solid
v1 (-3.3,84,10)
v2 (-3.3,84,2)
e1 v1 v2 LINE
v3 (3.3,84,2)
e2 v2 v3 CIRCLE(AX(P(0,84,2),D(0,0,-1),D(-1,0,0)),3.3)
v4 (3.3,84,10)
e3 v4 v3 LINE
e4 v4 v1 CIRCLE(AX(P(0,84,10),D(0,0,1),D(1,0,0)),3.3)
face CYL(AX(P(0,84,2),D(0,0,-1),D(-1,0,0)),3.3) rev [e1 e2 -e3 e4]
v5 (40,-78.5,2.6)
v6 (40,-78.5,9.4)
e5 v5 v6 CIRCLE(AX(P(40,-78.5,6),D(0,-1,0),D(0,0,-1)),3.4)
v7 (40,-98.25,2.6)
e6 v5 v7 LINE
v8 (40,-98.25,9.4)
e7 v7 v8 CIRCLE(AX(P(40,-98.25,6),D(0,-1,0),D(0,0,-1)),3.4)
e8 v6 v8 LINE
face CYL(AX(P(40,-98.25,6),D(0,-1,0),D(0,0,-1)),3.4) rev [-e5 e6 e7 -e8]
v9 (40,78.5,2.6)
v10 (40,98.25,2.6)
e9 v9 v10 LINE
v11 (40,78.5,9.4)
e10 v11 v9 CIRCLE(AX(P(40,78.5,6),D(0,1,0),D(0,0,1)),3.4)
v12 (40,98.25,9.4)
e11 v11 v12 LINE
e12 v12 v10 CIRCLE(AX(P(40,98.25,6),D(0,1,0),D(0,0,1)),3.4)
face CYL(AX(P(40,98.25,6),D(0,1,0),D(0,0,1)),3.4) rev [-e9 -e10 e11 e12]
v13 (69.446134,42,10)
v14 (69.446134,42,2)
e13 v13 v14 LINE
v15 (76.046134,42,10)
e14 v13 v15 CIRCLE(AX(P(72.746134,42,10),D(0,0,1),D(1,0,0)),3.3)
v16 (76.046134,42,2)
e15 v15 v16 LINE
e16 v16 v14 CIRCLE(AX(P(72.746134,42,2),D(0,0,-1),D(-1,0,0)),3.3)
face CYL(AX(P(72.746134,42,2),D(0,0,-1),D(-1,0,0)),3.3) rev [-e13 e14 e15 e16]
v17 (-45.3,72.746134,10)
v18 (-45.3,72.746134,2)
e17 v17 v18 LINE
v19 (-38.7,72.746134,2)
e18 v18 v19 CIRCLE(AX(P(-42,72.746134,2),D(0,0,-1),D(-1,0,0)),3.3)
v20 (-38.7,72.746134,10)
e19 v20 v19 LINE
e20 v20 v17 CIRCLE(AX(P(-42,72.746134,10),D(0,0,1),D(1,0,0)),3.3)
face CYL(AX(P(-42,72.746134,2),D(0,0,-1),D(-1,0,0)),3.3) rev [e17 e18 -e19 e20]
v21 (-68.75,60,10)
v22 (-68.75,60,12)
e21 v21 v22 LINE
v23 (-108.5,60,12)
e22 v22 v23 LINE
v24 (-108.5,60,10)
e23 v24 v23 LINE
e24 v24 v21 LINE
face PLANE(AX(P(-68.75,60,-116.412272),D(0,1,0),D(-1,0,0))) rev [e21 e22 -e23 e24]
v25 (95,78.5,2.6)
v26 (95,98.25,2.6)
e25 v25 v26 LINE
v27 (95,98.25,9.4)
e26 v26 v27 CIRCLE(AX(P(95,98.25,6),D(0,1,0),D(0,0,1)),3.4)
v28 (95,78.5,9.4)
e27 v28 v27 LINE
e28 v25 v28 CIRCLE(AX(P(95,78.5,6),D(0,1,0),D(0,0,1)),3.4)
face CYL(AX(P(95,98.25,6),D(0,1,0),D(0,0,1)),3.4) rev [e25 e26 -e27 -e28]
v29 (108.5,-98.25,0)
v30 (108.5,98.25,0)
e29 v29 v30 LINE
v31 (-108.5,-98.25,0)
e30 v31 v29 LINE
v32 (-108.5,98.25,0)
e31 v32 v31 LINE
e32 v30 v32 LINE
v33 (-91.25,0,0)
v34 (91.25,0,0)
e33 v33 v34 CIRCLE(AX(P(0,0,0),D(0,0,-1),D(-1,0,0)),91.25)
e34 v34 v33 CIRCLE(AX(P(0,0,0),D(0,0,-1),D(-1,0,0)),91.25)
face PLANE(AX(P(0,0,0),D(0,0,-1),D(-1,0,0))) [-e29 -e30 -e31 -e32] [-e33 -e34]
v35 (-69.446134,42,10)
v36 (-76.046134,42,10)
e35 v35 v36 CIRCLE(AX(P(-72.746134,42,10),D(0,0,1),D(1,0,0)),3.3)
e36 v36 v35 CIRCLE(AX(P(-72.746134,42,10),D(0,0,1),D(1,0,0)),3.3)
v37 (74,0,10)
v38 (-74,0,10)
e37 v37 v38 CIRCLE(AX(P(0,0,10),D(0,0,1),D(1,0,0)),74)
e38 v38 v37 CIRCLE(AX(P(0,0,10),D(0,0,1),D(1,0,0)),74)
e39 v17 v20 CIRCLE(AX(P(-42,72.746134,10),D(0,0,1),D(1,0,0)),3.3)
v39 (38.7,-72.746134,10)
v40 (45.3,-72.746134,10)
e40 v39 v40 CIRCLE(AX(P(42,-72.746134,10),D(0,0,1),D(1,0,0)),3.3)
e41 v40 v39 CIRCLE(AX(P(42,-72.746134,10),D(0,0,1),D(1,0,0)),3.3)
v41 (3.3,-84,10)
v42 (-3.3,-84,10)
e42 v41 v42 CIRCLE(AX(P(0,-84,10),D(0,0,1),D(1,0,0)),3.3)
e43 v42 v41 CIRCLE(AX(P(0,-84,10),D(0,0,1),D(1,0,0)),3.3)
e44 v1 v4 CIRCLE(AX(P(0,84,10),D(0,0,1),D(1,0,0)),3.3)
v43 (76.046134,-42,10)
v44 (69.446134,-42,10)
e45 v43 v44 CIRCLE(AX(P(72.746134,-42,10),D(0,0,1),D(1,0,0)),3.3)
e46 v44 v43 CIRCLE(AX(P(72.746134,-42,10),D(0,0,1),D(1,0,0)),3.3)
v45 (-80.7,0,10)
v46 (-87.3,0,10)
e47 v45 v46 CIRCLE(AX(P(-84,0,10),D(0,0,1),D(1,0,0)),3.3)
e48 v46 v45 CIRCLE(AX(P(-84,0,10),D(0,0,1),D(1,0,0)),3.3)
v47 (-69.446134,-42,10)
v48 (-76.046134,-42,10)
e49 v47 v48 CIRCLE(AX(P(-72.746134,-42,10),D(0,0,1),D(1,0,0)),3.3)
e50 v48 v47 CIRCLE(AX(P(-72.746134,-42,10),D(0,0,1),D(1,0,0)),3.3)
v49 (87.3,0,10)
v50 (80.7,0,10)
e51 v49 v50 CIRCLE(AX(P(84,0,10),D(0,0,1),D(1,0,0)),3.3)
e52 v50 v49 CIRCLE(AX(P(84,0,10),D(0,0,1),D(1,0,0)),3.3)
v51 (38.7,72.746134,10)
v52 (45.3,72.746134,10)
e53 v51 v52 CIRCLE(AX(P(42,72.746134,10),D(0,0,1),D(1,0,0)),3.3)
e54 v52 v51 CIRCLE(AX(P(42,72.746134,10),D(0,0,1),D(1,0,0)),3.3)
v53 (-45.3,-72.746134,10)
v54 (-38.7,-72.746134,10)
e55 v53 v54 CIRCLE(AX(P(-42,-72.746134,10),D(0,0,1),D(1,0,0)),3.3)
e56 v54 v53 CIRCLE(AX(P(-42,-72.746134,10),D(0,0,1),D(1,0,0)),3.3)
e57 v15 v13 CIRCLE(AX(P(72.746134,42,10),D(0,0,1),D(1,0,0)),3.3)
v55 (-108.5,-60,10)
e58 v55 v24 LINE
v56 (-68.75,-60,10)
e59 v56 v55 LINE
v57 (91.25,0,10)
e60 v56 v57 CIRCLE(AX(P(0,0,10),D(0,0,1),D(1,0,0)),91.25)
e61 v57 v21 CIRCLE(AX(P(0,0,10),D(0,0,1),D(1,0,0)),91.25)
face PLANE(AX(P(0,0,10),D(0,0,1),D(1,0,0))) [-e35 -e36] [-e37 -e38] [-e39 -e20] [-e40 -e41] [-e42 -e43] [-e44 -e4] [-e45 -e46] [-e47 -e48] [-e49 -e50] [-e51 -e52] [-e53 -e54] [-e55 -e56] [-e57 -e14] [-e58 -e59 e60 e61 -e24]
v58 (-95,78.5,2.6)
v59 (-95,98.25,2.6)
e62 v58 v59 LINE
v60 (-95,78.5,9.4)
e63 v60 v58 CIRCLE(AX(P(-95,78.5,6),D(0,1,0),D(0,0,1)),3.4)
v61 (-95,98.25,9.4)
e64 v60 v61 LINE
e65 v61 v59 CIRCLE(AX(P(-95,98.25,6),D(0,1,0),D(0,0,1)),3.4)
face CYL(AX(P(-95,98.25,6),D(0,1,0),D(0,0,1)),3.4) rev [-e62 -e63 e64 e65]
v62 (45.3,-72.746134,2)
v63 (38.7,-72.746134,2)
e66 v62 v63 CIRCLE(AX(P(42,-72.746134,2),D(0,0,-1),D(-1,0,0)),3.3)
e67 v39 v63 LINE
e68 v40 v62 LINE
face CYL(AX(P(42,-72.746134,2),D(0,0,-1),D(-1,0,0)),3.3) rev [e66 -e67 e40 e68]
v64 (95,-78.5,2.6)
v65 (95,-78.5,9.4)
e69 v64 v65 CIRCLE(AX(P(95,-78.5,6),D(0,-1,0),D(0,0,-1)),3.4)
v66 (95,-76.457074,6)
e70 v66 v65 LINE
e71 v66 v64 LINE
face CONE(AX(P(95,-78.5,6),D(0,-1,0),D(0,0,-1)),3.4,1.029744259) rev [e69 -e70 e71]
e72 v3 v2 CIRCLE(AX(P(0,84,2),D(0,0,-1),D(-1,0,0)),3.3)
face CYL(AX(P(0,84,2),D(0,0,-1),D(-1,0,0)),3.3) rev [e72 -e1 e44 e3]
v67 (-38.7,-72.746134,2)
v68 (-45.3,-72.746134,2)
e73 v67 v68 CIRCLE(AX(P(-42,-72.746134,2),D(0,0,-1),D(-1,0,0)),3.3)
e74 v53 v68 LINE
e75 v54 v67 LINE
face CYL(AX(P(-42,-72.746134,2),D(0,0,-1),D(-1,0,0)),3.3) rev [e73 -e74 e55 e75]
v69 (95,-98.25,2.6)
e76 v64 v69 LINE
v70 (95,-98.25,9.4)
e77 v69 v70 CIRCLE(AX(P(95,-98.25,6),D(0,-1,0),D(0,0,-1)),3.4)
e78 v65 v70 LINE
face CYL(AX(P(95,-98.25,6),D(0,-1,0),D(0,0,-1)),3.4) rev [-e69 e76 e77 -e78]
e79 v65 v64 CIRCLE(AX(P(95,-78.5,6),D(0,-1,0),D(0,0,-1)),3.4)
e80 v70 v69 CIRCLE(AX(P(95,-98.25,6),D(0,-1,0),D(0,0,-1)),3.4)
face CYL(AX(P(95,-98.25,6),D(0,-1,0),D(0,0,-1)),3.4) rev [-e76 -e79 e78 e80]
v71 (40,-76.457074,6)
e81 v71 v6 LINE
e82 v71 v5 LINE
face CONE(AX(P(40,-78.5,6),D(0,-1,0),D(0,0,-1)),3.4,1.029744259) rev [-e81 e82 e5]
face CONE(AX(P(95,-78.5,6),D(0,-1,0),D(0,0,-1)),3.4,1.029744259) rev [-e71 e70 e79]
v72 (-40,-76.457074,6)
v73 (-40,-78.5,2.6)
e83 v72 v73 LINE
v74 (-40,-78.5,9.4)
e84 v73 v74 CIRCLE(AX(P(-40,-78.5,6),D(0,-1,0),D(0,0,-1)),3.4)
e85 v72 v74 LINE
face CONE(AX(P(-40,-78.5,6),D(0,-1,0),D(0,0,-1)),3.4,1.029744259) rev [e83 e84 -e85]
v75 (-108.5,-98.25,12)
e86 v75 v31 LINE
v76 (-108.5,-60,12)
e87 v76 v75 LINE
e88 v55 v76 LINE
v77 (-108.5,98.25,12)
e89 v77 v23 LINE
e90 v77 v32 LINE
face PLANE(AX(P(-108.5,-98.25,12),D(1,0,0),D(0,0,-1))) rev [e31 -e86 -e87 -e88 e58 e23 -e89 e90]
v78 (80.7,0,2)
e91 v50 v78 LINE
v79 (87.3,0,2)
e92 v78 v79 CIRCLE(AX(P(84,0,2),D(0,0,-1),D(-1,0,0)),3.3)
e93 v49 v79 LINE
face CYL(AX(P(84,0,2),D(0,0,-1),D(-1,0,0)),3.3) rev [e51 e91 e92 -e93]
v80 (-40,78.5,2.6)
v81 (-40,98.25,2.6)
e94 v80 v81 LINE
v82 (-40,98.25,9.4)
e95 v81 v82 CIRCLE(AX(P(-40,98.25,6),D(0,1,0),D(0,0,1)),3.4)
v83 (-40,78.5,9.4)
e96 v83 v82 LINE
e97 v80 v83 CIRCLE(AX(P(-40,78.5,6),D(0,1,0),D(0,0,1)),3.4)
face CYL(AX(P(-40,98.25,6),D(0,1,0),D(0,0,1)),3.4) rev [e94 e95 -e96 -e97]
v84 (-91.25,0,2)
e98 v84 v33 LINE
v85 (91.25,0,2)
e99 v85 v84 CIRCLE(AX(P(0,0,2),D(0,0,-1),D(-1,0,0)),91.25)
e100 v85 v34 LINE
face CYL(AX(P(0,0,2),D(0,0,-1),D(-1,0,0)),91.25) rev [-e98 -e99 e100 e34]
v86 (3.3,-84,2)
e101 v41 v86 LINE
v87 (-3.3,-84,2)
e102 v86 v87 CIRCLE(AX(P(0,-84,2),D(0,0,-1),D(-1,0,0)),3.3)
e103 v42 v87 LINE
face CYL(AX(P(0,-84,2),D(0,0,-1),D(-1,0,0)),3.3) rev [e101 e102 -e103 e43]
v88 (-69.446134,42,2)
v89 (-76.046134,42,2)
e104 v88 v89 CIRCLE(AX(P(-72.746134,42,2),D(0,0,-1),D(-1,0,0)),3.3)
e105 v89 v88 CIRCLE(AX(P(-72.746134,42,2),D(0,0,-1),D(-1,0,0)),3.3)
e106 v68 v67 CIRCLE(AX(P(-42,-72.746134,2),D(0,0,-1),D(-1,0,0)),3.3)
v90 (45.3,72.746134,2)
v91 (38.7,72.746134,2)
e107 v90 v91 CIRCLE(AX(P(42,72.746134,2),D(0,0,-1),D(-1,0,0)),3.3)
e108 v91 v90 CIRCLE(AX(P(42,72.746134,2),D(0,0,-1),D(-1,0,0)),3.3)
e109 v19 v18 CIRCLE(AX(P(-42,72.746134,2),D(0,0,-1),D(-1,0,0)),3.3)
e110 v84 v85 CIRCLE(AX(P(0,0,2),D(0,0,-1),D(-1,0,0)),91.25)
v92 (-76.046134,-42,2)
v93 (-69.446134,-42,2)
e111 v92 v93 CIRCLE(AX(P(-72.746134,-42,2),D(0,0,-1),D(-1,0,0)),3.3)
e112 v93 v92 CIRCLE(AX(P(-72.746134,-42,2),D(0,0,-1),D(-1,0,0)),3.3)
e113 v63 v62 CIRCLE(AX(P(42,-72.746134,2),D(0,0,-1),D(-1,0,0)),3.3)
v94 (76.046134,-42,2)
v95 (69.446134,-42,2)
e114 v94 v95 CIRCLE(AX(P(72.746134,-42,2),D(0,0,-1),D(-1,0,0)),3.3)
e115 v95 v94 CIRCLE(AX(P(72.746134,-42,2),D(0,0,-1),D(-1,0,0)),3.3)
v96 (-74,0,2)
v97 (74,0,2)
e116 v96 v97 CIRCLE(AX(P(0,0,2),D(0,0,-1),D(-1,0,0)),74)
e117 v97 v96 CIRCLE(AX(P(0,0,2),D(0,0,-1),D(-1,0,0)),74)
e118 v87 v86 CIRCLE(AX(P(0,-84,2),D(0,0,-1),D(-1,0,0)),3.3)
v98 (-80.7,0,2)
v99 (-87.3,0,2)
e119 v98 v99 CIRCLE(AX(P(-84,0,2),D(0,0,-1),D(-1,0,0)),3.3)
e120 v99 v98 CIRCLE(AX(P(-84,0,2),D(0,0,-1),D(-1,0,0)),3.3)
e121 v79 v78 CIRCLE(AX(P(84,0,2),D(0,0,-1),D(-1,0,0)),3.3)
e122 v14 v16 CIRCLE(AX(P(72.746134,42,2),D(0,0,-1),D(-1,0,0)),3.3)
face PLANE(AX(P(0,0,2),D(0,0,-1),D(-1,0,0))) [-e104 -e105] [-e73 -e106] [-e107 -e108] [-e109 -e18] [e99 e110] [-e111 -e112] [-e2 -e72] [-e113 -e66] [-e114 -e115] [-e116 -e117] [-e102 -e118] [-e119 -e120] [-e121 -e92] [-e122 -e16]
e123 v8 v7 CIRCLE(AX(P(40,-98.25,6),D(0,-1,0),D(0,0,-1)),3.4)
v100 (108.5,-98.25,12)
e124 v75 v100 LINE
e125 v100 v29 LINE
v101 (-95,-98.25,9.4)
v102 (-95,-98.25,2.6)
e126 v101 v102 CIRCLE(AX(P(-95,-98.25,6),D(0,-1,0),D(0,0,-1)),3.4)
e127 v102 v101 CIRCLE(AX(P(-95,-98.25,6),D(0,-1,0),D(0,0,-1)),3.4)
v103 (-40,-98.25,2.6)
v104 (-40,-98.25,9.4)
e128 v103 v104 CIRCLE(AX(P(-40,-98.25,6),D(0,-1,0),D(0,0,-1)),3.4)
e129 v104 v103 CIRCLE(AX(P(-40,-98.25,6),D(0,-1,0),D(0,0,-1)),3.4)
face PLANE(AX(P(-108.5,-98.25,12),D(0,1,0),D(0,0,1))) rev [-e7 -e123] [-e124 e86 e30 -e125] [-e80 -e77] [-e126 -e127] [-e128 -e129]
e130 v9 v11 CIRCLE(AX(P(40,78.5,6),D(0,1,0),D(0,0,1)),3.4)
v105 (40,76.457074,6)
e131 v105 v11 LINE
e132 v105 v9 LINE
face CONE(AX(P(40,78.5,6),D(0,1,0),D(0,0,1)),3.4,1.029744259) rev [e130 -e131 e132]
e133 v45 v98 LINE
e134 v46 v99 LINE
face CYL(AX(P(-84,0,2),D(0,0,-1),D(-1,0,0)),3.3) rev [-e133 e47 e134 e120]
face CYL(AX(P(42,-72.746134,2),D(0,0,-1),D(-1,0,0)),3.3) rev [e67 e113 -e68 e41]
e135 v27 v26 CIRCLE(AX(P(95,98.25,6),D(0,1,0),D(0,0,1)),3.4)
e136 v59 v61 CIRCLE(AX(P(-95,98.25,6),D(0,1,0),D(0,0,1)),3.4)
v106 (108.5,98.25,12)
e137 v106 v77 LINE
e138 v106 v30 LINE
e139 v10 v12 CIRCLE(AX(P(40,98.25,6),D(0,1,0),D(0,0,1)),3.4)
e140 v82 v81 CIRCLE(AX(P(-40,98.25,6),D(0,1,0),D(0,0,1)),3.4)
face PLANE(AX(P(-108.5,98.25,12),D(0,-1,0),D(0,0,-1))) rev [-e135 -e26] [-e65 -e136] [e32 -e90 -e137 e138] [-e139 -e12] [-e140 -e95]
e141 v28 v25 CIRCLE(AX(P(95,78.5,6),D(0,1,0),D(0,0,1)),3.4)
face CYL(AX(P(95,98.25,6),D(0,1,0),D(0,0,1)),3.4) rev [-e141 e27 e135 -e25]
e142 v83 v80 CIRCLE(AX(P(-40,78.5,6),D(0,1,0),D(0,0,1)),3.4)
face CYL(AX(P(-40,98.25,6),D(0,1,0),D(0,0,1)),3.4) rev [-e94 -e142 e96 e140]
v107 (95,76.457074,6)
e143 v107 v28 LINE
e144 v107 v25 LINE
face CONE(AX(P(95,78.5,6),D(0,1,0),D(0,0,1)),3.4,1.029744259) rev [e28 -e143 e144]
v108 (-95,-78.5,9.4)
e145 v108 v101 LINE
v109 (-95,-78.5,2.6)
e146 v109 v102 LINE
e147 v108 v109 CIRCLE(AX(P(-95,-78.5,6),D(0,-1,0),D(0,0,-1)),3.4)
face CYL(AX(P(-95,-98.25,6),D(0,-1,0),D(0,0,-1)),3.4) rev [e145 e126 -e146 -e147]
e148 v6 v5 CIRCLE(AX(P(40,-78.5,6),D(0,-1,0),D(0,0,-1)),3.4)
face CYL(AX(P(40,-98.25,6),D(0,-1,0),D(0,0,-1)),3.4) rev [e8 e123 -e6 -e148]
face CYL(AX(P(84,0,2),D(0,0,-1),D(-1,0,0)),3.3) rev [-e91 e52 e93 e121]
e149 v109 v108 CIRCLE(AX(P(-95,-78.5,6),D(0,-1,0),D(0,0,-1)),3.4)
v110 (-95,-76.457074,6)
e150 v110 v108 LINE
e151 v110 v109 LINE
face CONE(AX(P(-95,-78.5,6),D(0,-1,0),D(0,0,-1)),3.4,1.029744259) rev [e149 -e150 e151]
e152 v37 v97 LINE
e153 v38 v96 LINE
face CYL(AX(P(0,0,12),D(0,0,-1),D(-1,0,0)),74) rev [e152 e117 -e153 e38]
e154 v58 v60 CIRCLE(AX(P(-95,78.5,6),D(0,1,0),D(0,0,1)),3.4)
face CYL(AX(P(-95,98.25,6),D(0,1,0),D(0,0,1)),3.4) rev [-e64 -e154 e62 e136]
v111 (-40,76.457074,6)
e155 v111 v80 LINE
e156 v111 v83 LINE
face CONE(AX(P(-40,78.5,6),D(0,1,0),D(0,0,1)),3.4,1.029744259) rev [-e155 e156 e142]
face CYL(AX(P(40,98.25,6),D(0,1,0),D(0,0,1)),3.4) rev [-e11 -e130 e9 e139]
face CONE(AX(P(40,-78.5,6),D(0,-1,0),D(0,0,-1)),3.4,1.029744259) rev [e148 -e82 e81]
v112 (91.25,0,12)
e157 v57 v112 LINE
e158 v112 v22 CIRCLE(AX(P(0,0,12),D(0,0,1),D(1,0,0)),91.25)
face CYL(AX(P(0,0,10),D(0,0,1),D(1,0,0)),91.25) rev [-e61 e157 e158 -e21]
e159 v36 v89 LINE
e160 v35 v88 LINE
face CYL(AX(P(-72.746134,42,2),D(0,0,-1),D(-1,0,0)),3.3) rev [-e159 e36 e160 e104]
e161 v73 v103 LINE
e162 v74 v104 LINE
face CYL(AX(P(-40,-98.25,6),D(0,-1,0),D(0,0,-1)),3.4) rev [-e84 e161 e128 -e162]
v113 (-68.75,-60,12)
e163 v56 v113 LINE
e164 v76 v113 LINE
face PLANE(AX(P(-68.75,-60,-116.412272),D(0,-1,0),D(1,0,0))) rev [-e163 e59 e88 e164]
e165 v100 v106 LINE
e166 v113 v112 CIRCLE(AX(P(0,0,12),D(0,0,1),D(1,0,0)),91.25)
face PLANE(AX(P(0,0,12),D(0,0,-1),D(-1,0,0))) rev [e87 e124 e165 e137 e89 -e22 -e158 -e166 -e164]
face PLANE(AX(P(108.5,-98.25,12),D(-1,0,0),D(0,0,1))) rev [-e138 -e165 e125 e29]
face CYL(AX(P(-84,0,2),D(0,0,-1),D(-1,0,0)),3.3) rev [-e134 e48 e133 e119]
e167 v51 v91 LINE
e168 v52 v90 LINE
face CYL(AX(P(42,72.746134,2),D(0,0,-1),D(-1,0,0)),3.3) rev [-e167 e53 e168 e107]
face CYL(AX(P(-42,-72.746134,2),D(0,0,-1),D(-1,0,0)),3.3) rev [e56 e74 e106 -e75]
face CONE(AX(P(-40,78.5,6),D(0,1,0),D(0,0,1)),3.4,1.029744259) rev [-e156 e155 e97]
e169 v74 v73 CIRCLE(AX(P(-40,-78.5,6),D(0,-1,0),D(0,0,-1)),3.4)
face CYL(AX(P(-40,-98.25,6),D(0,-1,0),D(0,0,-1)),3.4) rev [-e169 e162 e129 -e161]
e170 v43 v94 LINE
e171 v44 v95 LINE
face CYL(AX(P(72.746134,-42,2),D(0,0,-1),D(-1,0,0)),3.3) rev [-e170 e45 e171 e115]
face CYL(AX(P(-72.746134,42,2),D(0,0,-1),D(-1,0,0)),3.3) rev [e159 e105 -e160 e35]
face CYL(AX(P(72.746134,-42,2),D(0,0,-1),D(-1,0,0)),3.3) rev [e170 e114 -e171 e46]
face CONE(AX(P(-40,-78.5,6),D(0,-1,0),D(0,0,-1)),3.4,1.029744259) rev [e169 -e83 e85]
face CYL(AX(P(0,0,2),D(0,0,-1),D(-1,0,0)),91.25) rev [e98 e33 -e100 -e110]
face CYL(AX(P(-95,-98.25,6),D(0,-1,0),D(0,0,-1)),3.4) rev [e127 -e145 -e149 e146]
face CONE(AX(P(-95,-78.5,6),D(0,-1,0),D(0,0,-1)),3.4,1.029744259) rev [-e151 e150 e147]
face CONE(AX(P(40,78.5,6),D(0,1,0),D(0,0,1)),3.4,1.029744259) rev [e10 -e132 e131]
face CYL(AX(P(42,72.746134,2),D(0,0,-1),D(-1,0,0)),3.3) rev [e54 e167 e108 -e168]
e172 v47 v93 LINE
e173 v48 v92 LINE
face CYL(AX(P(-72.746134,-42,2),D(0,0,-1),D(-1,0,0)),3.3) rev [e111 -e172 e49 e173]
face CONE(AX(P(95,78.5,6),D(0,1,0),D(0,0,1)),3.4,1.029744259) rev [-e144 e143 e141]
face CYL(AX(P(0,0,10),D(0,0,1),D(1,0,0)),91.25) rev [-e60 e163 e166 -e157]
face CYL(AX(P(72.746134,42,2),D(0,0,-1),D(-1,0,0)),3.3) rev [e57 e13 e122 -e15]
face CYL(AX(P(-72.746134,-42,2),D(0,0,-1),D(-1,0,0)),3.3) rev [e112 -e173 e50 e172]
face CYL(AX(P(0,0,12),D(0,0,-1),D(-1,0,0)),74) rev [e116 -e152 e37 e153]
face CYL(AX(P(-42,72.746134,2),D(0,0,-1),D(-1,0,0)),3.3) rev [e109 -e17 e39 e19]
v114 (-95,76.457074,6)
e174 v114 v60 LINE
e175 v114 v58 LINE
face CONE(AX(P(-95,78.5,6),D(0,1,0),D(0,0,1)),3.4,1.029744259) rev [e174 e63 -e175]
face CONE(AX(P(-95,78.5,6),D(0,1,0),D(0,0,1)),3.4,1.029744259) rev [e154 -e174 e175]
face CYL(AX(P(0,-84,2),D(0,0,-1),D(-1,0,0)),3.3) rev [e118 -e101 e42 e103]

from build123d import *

# Parameters (mm, degrees)
SKETCH_1_W             = 217
SKETCH_1_H             = 196.5
SKETCH_1_R             = 74
EXTRUDE_1_DEPTH        = 12
SKETCH_2_R             = 91.25
CUT_EXTRUDE_1_DEPTH    = 2
CUT_EXTRUDE_START      = -2
SKETCH_3_R             = 91.25
CUT_EXTRUDE_2_DEPTH    = 2
SKETCH_4_W             = 39.75
SKETCH_4_H             = 120
CUT_EXTRUDE_3_DEPTH    = 2
HOLE_WIZARD_M6_1_D     = 6.6
HOLE_WIZARD_M8_1_D     = 6.8
HOLE_WIZARD_M8_1_DEPTH = 19.75
HOLE_WIZARD_M8_1_TIP   = 2.042926105
HOLE_WIZARD_M8_2_D     = 6.8
HOLE_WIZARD_M8_2_DEPTH = 19.75
HOLE_WIZARD_M8_2_TIP   = 2.042926105


with BuildPart() as part:
    # 草图1 → 凸台-拉伸1 (new body)
    with BuildSketch(Plane.XY):
        Rectangle(SKETCH_1_W, SKETCH_1_H)
        Circle(SKETCH_1_R, mode=Mode.SUBTRACT)
    extrude(amount=EXTRUDE_1_DEPTH)

    # 草图2 → 切除-拉伸1 (cut)
    with BuildSketch(Plane(origin=(0, 0, 0), x_dir=(-1, 0, 0), z_dir=(0, 0, -1))):
        Circle(SKETCH_2_R)
    extrude(amount=-CUT_EXTRUDE_1_DEPTH, mode=Mode.SUBTRACT)

    # 草图3 → 切除-拉伸2 (cut)
    with BuildSketch(Plane.XY.offset(12).offset(CUT_EXTRUDE_START)):
        with Locations(Location((0, 0, 0), (0, 0, 180))):
            Circle(SKETCH_3_R)
    extrude(amount=CUT_EXTRUDE_2_DEPTH, mode=Mode.SUBTRACT)

    # 草图4 → 切除-拉伸3 (cut)
    with BuildSketch(Plane.XY.offset(12)):
        with Locations((-88.625, 0)):
            Rectangle(SKETCH_4_W, SKETCH_4_H)
    extrude(amount=-CUT_EXTRUDE_3_DEPTH, mode=Mode.SUBTRACT)

    # M6 间隙孔1 (through all)
    with Locations(Plane(origin=(0, 0, 2), x_dir=(-1, 0, 0), z_dir=(0, 0, -1))):
        with Locations((0, 84), (42, 72.746133918), (72.746133918, 42), (84, 0), (72.746133918, -42), (42, -72.746133918), (0, -84), (-42, -72.746133918), (-72.746133918, -42), (-84, 0), (-72.746133918, 42), (-42, 72.746133918)):
            Hole(HOLE_WIZARD_M6_1_D / 2)

    # M8 螺纹孔1
    with Locations(Plane(origin=(0, -98.25, 0), x_dir=(-1, 0, 0), z_dir=(0, -1, 0))):
        with Locations((-95, -6), (-40, -6), (40, -6), (95, -6)):
            Hole(HOLE_WIZARD_M8_1_D / 2, depth=HOLE_WIZARD_M8_1_DEPTH)
            with Locations((0, 0, -(HOLE_WIZARD_M8_1_DEPTH + HOLE_WIZARD_M8_1_TIP / 2))):  # 118° drill point
                Cone(0, HOLE_WIZARD_M8_1_D / 2, HOLE_WIZARD_M8_1_TIP, mode=Mode.SUBTRACT)

    # M8 螺纹孔2
    with Locations(Plane(origin=(0, 98.25, 0), x_dir=(1, 0, 0), z_dir=(0, 1, 0))):
        with Locations((-95, -6), (-40, -6), (40, -6), (95, -6)):
            Hole(HOLE_WIZARD_M8_2_D / 2, depth=HOLE_WIZARD_M8_2_DEPTH)
            with Locations((0, 0, -(HOLE_WIZARD_M8_2_DEPTH + HOLE_WIZARD_M8_2_TIP / 2))):  # 118° drill point
                Cone(0, HOLE_WIZARD_M8_2_D / 2, HOLE_WIZARD_M8_2_TIP, mode=Mode.SUBTRACT)


solid = part.part
